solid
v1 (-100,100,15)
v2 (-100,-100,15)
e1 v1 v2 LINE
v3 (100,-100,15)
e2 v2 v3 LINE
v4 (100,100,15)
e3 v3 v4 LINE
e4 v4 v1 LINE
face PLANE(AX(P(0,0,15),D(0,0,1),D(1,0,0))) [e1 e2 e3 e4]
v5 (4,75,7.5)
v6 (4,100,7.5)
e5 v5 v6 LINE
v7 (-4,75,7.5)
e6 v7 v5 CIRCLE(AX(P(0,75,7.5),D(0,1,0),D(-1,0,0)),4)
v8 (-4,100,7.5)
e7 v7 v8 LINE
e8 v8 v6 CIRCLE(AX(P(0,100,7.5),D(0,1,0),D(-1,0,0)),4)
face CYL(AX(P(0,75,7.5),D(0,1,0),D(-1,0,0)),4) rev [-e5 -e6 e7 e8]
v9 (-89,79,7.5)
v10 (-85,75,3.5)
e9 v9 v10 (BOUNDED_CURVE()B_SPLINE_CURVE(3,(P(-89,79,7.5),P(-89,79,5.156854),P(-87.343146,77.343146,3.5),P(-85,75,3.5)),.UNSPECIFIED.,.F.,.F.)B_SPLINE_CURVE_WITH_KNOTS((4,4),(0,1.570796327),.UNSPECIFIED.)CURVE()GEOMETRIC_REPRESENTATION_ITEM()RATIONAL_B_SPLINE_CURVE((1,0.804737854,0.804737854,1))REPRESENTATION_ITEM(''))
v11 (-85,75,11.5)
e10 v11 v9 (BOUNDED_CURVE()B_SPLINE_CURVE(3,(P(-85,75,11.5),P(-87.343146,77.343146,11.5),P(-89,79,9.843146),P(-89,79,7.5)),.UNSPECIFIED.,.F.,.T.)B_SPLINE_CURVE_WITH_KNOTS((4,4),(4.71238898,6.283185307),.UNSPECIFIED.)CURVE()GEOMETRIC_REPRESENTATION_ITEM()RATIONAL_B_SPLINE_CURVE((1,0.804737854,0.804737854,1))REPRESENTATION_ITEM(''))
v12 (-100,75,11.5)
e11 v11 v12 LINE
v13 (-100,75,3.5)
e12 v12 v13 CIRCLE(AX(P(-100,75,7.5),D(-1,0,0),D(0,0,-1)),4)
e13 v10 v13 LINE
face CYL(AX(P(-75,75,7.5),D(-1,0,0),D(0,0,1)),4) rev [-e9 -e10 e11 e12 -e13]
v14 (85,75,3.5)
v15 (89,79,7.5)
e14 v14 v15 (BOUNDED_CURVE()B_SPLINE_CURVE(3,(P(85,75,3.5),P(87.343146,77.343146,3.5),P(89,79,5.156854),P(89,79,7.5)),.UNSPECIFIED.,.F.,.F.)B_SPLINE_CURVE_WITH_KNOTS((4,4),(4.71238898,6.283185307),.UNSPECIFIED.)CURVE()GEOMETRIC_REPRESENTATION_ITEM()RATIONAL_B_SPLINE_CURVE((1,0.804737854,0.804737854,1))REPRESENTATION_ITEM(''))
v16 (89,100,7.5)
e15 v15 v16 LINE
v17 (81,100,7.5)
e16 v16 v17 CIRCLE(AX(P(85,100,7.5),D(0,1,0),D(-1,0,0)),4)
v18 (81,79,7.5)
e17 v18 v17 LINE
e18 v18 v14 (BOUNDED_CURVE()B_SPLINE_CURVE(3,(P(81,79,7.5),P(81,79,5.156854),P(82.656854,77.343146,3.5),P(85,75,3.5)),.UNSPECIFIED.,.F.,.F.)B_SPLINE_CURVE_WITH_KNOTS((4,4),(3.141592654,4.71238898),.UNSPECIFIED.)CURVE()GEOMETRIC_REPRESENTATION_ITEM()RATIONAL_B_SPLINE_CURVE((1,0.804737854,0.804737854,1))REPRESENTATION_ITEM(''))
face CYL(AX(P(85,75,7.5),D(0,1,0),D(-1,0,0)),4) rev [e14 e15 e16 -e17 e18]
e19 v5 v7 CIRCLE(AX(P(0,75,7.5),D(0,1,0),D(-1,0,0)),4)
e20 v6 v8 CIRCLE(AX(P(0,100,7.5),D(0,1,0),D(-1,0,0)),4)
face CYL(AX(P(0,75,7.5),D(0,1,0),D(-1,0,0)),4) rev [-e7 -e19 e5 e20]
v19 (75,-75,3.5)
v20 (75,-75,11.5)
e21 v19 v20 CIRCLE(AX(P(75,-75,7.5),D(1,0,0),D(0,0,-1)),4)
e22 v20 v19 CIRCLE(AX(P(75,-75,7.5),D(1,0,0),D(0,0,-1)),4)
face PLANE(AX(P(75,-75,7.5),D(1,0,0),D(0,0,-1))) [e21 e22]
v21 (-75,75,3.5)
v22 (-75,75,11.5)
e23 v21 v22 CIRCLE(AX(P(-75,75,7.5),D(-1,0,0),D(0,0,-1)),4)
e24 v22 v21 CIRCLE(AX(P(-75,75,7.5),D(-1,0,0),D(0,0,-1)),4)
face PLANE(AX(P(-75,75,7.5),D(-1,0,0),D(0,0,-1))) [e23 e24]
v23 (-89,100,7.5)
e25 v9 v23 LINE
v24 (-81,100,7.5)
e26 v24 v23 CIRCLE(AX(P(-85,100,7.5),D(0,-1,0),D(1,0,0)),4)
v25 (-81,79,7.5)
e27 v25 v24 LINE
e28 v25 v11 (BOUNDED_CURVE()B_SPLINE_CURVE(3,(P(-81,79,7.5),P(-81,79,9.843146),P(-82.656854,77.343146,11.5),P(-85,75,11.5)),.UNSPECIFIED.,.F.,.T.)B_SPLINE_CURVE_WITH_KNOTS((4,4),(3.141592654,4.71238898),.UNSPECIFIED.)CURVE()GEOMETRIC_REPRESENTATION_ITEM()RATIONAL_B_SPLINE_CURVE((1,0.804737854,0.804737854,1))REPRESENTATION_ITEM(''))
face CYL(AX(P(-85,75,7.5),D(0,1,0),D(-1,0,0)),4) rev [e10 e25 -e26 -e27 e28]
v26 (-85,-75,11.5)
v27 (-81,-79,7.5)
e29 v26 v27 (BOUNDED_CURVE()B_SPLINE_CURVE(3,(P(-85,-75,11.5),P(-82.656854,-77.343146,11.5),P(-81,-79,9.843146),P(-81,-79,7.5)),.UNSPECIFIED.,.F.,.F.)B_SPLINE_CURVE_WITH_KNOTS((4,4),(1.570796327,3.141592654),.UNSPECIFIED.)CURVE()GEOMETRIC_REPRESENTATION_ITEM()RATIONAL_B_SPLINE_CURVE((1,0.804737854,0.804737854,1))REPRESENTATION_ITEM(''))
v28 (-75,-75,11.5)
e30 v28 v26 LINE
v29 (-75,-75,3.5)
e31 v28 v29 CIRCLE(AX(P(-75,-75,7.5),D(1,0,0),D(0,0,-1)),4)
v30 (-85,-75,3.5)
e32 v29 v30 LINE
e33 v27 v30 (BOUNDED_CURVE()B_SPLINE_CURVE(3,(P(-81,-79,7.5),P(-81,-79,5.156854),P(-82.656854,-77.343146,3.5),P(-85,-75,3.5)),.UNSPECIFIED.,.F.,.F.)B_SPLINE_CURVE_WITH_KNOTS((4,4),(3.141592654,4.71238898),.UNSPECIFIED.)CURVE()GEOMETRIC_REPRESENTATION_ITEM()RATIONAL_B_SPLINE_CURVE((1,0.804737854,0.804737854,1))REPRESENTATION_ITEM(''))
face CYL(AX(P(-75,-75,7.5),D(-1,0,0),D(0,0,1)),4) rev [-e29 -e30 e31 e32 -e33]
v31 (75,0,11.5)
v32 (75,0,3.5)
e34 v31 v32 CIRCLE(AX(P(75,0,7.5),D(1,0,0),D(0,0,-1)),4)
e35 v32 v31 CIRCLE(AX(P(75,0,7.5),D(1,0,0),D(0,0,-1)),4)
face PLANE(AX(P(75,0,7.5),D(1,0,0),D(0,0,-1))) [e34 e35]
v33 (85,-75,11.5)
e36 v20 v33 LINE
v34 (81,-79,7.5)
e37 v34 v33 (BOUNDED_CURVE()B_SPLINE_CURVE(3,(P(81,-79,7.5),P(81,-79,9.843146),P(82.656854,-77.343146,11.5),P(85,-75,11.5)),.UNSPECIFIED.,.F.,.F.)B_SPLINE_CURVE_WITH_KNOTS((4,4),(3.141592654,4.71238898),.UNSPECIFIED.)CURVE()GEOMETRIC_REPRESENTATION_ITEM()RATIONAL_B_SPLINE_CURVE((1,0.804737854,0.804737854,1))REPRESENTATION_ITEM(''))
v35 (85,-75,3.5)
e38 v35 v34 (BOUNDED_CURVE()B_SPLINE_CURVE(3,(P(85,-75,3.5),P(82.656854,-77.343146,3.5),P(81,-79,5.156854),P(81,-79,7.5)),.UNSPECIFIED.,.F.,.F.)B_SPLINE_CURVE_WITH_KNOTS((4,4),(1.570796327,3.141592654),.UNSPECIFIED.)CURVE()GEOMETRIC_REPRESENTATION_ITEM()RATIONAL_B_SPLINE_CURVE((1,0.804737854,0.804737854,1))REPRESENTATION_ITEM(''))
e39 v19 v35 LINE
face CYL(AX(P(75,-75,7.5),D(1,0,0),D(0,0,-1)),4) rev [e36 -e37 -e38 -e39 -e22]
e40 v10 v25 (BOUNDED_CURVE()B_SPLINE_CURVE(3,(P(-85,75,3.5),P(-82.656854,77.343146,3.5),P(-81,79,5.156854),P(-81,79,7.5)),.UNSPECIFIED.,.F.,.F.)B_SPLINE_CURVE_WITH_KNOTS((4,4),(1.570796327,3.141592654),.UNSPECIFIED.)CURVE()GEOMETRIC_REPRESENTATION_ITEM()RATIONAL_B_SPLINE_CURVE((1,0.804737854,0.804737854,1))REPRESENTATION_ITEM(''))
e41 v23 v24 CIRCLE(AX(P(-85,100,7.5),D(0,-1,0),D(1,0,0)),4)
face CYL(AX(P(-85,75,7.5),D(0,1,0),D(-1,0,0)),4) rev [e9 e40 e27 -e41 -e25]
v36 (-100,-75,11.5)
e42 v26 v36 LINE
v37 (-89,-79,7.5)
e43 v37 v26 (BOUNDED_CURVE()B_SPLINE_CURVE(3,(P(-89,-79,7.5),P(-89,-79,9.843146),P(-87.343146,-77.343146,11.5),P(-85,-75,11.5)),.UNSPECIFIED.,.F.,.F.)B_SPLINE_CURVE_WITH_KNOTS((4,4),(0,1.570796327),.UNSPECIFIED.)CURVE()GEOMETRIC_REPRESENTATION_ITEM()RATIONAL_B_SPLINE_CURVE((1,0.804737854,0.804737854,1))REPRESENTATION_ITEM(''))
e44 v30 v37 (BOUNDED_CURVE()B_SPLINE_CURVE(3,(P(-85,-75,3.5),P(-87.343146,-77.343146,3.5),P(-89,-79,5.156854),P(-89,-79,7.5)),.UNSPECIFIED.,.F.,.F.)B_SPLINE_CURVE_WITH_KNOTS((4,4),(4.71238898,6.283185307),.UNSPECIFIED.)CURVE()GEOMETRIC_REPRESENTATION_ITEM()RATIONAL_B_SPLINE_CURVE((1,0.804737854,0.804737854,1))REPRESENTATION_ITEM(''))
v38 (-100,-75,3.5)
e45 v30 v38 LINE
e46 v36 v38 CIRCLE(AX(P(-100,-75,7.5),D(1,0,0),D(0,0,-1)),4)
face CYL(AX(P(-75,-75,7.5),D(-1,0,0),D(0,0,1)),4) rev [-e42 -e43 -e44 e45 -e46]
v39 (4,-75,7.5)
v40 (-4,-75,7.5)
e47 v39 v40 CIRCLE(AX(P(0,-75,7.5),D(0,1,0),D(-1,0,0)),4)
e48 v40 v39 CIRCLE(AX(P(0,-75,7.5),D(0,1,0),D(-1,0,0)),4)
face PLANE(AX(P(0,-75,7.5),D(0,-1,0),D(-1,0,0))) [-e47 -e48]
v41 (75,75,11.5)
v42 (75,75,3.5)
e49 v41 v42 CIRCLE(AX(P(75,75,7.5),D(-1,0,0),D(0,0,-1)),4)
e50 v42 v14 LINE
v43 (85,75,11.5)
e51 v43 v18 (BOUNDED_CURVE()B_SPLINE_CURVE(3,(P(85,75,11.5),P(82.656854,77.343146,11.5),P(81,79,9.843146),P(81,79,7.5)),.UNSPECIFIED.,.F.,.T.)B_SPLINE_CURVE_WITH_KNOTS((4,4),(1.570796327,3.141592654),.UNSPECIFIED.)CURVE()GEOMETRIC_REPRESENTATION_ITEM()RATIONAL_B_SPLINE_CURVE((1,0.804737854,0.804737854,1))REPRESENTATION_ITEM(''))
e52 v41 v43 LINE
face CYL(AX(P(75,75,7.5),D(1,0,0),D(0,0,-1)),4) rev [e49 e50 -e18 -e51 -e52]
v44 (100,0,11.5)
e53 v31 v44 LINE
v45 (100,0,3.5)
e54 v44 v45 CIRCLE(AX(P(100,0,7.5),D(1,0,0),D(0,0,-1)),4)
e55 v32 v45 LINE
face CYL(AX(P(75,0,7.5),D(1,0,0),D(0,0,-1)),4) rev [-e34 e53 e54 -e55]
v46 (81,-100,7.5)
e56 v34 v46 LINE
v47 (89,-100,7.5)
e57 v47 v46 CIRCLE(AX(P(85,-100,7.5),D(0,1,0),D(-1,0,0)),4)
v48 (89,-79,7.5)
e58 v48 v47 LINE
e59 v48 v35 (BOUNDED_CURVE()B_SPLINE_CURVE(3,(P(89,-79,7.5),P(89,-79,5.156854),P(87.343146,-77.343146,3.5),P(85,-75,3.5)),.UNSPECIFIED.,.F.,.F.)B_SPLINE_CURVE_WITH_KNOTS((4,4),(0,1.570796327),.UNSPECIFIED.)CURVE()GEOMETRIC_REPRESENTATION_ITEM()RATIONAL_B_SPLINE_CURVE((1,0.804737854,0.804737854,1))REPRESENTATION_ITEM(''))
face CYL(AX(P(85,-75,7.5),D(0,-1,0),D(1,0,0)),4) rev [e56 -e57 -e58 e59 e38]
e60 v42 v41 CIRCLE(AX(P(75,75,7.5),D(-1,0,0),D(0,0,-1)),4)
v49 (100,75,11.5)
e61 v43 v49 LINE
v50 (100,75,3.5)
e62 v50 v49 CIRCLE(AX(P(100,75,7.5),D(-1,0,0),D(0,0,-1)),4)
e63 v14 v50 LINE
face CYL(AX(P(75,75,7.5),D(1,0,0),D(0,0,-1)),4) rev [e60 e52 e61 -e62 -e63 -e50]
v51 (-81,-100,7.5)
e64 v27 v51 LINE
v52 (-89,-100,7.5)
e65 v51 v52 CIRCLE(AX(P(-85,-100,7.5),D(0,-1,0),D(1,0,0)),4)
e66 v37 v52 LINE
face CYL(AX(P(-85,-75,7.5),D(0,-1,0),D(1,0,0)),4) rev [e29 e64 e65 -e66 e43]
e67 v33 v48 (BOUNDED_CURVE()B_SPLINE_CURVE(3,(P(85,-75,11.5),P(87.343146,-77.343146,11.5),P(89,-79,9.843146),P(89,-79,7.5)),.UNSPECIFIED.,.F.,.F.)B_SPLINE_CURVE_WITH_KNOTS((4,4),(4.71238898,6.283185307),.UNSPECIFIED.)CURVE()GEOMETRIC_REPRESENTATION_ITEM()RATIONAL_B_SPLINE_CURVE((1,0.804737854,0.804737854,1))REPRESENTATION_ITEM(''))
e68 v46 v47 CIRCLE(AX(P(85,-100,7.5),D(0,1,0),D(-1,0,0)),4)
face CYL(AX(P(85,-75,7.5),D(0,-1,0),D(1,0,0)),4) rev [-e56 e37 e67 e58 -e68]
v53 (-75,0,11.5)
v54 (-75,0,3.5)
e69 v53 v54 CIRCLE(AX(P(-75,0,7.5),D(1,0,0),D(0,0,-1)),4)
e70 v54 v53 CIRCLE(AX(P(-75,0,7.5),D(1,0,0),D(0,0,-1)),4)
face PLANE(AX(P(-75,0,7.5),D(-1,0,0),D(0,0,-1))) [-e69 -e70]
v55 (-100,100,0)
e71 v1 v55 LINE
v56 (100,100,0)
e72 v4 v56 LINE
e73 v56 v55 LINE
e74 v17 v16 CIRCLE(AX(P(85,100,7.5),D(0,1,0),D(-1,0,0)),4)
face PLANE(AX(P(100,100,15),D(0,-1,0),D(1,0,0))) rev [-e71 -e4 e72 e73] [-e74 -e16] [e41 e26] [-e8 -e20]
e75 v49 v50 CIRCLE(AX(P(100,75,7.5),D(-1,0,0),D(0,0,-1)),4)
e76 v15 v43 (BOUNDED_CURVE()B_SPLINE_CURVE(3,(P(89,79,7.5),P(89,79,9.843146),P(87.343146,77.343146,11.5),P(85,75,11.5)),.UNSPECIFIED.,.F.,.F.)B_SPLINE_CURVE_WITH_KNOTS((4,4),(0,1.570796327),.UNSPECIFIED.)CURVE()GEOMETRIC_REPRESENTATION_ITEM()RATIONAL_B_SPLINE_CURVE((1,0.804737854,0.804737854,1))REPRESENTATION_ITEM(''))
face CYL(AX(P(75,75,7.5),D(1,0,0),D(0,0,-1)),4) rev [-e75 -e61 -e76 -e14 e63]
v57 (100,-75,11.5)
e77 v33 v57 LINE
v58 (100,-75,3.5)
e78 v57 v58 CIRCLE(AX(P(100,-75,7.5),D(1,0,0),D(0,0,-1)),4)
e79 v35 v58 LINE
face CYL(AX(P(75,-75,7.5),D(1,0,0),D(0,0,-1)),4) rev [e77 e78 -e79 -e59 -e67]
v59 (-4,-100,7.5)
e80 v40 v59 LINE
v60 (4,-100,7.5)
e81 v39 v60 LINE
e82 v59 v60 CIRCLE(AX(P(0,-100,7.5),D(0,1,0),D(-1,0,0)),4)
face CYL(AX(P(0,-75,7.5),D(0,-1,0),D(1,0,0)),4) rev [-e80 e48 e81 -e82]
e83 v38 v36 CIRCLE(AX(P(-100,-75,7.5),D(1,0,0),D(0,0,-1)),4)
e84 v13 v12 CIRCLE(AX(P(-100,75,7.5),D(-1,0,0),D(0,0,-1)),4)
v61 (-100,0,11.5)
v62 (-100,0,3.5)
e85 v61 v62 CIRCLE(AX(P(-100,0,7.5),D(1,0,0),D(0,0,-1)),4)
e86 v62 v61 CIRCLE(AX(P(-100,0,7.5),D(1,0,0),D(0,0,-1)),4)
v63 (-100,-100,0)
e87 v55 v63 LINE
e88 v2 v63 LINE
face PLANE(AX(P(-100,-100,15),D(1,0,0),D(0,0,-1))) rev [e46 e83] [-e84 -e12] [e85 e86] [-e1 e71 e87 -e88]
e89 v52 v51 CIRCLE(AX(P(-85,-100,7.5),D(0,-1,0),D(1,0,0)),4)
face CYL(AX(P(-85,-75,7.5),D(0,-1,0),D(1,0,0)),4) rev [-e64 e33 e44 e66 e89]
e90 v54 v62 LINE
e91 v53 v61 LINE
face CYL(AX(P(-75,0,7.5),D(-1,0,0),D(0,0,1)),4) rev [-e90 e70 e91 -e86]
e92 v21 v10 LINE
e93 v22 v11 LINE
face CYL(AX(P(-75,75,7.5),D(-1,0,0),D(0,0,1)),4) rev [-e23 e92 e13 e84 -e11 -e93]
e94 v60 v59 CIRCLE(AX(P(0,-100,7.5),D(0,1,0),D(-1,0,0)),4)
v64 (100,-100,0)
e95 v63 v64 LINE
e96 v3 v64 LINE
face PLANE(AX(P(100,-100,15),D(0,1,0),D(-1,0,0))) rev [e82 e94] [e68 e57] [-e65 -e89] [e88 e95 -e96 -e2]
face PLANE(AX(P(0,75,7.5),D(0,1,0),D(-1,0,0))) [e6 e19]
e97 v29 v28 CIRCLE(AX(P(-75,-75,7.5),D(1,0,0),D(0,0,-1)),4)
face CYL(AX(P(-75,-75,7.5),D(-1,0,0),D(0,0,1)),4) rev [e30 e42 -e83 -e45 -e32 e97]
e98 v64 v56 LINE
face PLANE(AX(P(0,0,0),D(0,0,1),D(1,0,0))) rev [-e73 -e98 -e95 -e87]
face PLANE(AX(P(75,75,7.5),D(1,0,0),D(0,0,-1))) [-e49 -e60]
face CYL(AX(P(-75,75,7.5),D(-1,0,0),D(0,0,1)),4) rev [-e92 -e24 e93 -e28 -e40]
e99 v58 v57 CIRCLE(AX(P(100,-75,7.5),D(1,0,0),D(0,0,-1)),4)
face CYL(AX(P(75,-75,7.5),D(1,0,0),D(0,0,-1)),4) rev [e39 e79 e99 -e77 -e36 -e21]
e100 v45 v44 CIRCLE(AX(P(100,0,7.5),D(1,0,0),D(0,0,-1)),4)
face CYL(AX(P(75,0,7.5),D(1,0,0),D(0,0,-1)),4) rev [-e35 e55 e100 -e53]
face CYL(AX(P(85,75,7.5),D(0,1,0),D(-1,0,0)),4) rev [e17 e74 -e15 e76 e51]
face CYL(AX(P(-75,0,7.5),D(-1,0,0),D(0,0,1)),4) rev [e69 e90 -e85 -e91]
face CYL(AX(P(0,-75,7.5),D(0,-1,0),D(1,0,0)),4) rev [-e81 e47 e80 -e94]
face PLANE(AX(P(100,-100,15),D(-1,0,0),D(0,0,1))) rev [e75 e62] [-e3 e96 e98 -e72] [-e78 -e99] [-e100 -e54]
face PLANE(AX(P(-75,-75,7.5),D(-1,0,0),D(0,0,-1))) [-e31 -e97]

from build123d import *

# Parameters (mm, degrees)
SKETCH1_W               = 200
SKETCH1_H               = 200
BOSS_EXTRUDE1_DEPTH     = 15
SKETCH2_R               = 4
CUT_EXTRUDE1_DEPTH      = 25
LPATTERN1_COUNT         = 2
LPATTERN1_PITCH         = 75
MIRROR1_COPY_1_SKETCH_R = 4
MIRROR1_COPY_1_DEPTH    = 25
MIRROR2_COPY_1_SKETCH_R = 4
MIRROR2_COPY_1_DEPTH    = 25
MIRROR2_COPY_2_SKETCH_R = 4
MIRROR2_COPY_2_DEPTH    = 25
MIRROR2_COPY_3_SKETCH_R = 4
MIRROR2_COPY_3_DEPTH    = 25
SKETCH3_R               = 4
CUT_EXTRUDE2_DEPTH      = 25
LPATTERN2_COUNT         = 2
LPATTERN2_PITCH         = 85
MIRROR3_COPY_1_SKETCH_R = 4
MIRROR3_COPY_1_DEPTH    = 25
MIRROR4_COPY_1_SKETCH_R = 4
MIRROR4_COPY_1_DEPTH    = 25
MIRROR4_COPY_2_SKETCH_R = 4
MIRROR4_COPY_2_DEPTH    = 25
MIRROR4_COPY_3_SKETCH_R = 4
MIRROR4_COPY_3_DEPTH    = 25


with BuildPart() as part:
    # Sketch1 → Boss-Extrude1 (new body)
    with BuildSketch(Plane.XY):
        Rectangle(SKETCH1_W, SKETCH1_H)
    extrude(amount=BOSS_EXTRUDE1_DEPTH)

    # Sketch2 → Cut-Extrude1 (cut)
    with BuildSketch(Plane(origin=(100, 0, 0), x_dir=(0, 0, -1), z_dir=(1, 0, 0))):
        with Locations((-7.5, 0)):
            Circle(SKETCH2_R)
    cut_extrude1 = extrude(amount=-CUT_EXTRUDE1_DEPTH, mode=Mode.SUBTRACT)

    # LPattern1: Cut-Extrude1 ×2
    with Locations(*[(0, -i * LPATTERN1_PITCH, 0) for i in range(1, LPATTERN1_COUNT)]):
        add(cut_extrude1, mode=Mode.SUBTRACT)

    # Mirror1: Cut-Extrude1 across plane
    add(cut_extrude1.mirror(Plane.ZX), mode=Mode.SUBTRACT)

    # Mirror1 copy 1 sketch → Mirror1 copy 1 (cut)
    with BuildSketch(Plane(origin=(100, 75, 0), x_dir=(0, 0, -1), z_dir=(1, 0, 0))):
        with Locations((-7.5, 0)):
            Circle(MIRROR1_COPY_1_SKETCH_R)
    extrude(amount=-MIRROR1_COPY_1_DEPTH, mode=Mode.SUBTRACT)

    # Mirror2: Cut-Extrude1 across plane
    add(cut_extrude1.mirror(Plane(origin=(0, 0, 0), x_dir=(0, 0, 1), z_dir=(1, 0, 0))), mode=Mode.SUBTRACT)

    # Mirror2 copy 1 sketch → Mirror2 copy 1 (cut)
    with BuildSketch(Plane(origin=(-100, -75, 0), x_dir=(0, 0, -1), z_dir=(-1, 0, 0))):
        with Locations((-7.5, 0)):
            Circle(MIRROR2_COPY_1_SKETCH_R)
    extrude(amount=-MIRROR2_COPY_1_DEPTH, mode=Mode.SUBTRACT)

    # Mirror2 copy 2 sketch → Mirror2 copy 2 (cut)
    with BuildSketch(Plane(origin=(-100, 0, 0), x_dir=(0, 0, -1), z_dir=(-1, 0, 0))):
        with Locations((-7.5, 0)):
            Circle(MIRROR2_COPY_2_SKETCH_R)
    extrude(amount=-MIRROR2_COPY_2_DEPTH, mode=Mode.SUBTRACT)

    # Mirror2 copy 3 sketch → Mirror2 copy 3 (cut)
    with BuildSketch(Plane(origin=(-100, 75, 0), x_dir=(0, 0, -1), z_dir=(-1, 0, 0))):
        with Locations((-7.5, 0)):
            Circle(MIRROR2_COPY_3_SKETCH_R)
    extrude(amount=-MIRROR2_COPY_3_DEPTH, mode=Mode.SUBTRACT)

    # Sketch3 → Cut-Extrude2 (cut)
    with BuildSketch(Plane(origin=(0, 100, 0), x_dir=(1, 0, 0), z_dir=(0, 1, 0))):
        with Locations(Location((0, -7.5, 0), (0, 0, 180))):
            Circle(SKETCH3_R)
    cut_extrude2 = extrude(amount=-CUT_EXTRUDE2_DEPTH, mode=Mode.SUBTRACT)

    # LPattern2: Cut-Extrude2 ×2
    with Locations(*[(i * LPATTERN2_PITCH, 0, 0) for i in range(1, LPATTERN2_COUNT)]):
        add(cut_extrude2, mode=Mode.SUBTRACT)

    # Mirror3: Cut-Extrude2 across plane
    add(cut_extrude2.mirror(Plane(origin=(0, 0, 0), x_dir=(0, 0, 1), z_dir=(1, 0, 0))), mode=Mode.SUBTRACT)

    # Mirror3 copy 1 sketch → Mirror3 copy 1 (cut)
    with BuildSketch(Plane(origin=(-85, 100, 0), x_dir=(-1, 0, 0), z_dir=(0, 1, 0))):
        with Locations((0, 7.5)):
            Circle(MIRROR3_COPY_1_SKETCH_R)
    extrude(amount=-MIRROR3_COPY_1_DEPTH, mode=Mode.SUBTRACT)

    # Mirror4: Cut-Extrude2 across plane
    add(cut_extrude2.mirror(Plane.ZX), mode=Mode.SUBTRACT)

    # Mirror4 copy 1 sketch → Mirror4 copy 1 (cut)
    with BuildSketch(Plane(origin=(85, -100, 0), x_dir=(1, 0, 0), z_dir=(0, -1, 0))):
        with Locations((0, 7.5)):
            Circle(MIRROR4_COPY_1_SKETCH_R)
    extrude(amount=-MIRROR4_COPY_1_DEPTH, mode=Mode.SUBTRACT)

    # Mirror4 copy 2 sketch → Mirror4 copy 2 (cut)
    with BuildSketch(Plane(origin=(0, -100, 0), x_dir=(-1, 0, 0), z_dir=(0, -1, 0))):
        with Locations(Location((0, -7.5, 0), (0, 0, 180))):
            Circle(MIRROR4_COPY_2_SKETCH_R)
    extrude(amount=-MIRROR4_COPY_2_DEPTH, mode=Mode.SUBTRACT)

    # Mirror4 copy 3 sketch → Mirror4 copy 3 (cut)
    with BuildSketch(Plane(origin=(-85, -100, 0), x_dir=(-1, 0, 0), z_dir=(0, -1, 0))):
        with Locations(Location((0, -7.5, 0), (0, 0, 180))):
            Circle(MIRROR4_COPY_3_SKETCH_R)
    extrude(amount=-MIRROR4_COPY_3_DEPTH, mode=Mode.SUBTRACT)


solid = part.part
